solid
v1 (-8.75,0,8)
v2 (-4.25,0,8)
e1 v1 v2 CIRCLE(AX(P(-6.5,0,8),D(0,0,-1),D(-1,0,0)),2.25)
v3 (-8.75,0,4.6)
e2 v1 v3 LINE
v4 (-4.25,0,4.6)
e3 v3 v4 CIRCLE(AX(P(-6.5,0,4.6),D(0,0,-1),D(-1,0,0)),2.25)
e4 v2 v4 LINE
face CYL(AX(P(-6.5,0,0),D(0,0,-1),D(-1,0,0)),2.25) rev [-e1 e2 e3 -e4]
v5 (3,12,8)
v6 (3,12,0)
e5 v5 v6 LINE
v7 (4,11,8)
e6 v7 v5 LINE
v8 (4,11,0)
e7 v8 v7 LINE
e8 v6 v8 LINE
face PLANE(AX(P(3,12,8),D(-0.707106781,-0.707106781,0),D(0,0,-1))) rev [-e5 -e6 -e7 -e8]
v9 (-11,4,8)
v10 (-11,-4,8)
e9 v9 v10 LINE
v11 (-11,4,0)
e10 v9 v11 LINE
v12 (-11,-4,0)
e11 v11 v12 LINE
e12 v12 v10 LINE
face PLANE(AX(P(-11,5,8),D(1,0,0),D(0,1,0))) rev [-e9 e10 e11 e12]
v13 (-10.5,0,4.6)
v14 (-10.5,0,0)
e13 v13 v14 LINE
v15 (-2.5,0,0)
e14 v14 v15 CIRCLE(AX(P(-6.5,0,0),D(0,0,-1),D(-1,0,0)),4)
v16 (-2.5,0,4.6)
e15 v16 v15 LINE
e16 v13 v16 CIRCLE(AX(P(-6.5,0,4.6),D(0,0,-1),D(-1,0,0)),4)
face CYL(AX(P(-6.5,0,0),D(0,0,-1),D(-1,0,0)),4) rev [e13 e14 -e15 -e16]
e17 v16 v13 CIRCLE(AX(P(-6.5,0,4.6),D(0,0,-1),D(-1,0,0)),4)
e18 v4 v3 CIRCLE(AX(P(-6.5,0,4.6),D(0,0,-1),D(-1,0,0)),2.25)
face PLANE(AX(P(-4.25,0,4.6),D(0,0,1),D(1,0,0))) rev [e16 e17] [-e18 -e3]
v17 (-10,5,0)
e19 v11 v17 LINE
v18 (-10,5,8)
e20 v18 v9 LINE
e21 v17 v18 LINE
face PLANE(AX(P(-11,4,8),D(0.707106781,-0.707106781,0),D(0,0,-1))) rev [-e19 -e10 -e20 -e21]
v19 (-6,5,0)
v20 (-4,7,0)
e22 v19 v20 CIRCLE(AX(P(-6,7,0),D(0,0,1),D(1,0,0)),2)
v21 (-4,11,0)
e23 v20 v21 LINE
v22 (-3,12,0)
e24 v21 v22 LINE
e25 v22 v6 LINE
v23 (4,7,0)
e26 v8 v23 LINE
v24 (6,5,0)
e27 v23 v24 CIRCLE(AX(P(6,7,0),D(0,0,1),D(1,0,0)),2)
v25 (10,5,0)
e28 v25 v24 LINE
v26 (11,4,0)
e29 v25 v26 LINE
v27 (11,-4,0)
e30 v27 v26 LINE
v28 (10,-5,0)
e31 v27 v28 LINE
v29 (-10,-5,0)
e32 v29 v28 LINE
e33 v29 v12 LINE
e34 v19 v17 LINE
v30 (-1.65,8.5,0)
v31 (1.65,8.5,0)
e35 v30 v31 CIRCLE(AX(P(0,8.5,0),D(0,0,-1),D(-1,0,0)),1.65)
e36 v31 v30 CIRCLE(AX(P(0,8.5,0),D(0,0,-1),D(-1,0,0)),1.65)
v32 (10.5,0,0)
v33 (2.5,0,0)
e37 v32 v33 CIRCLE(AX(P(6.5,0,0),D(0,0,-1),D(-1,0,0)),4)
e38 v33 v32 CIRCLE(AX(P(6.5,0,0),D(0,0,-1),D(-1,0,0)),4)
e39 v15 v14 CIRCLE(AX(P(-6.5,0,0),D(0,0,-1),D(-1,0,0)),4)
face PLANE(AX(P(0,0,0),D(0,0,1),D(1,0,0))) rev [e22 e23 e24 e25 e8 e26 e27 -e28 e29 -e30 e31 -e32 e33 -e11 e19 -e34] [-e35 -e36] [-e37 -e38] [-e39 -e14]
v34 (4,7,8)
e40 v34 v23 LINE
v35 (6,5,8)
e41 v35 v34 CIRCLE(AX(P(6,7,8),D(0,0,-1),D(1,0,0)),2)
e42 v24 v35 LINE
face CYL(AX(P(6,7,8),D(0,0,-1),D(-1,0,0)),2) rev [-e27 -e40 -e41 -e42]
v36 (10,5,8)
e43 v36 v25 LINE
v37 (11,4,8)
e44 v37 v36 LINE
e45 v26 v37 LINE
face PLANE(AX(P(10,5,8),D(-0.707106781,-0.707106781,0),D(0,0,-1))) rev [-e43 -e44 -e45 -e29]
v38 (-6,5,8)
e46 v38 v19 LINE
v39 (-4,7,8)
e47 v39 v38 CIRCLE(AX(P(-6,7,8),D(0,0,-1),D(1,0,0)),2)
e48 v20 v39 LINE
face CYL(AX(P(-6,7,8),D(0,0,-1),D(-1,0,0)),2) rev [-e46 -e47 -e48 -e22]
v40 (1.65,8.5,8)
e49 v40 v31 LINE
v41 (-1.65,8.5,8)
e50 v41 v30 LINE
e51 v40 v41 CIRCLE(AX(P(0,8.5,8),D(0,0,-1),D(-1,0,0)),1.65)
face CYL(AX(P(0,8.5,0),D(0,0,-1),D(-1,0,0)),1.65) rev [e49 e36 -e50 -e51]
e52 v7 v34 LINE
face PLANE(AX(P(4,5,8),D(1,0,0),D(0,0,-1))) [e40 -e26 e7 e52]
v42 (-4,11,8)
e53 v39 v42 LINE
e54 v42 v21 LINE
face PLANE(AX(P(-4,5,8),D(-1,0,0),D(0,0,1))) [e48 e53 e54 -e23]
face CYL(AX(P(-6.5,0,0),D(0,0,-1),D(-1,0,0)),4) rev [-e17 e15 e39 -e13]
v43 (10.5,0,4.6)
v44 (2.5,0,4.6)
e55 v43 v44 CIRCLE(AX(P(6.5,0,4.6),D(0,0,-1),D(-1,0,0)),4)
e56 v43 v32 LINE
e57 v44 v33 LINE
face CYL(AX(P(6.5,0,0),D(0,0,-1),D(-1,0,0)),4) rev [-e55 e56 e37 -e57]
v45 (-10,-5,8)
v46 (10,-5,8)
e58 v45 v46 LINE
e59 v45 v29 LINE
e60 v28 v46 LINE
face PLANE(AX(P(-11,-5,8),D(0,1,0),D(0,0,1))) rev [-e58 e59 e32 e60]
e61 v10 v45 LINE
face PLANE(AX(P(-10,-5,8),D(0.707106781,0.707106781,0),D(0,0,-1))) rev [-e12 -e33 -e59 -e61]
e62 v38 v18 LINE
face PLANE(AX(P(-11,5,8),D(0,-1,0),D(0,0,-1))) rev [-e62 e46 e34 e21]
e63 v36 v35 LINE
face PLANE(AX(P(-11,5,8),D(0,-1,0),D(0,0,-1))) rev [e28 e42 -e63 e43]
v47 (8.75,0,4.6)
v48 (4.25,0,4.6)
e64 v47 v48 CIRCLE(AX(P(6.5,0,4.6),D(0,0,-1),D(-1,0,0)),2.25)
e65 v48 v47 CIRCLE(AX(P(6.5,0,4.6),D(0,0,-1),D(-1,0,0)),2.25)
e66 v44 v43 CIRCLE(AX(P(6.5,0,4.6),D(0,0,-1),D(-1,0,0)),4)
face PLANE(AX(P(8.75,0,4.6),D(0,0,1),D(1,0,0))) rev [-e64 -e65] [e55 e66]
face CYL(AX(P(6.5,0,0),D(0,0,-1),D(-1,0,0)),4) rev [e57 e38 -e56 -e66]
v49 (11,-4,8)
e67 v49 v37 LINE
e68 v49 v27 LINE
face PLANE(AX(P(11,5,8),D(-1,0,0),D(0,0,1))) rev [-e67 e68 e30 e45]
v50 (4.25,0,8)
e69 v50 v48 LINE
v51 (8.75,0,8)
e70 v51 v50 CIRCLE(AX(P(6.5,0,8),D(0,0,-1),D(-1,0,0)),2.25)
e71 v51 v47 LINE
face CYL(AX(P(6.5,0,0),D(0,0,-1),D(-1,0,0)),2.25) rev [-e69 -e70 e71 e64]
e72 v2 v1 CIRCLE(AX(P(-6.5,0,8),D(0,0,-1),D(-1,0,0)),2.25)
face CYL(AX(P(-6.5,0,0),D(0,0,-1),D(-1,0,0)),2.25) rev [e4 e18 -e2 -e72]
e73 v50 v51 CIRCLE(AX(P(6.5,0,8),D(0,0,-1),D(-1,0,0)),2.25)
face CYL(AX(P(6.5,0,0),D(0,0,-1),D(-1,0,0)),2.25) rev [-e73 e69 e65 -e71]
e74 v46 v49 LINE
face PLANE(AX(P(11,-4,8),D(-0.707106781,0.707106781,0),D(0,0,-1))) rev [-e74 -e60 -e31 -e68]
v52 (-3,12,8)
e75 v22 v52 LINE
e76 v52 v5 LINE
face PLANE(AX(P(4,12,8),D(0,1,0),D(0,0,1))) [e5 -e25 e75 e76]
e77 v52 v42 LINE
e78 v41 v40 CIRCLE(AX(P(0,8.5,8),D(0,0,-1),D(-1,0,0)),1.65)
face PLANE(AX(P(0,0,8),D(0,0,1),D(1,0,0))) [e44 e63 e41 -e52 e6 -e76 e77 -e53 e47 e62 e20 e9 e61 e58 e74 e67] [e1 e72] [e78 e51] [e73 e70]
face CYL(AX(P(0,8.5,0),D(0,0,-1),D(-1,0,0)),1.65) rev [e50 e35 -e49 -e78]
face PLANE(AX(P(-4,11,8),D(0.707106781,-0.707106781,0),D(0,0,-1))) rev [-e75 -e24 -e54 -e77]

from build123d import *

# Parameters (mm, degrees)
SKETCH1_W                                            = 22
SKETCH1_H                                            = 10
BOSS_EXTRUDE1_DEPTH                                  = 8
CBORE_FOR_M4_HEXAGON_SOCKET_HEAD_CAP_SCR_D           = 4.5
CBORE_FOR_M4_HEXAGON_SOCKET_HEAD_CAP_SCR_CBORE_D     = 8
CBORE_FOR_M4_HEXAGON_SOCKET_HEAD_CAP_SCR_CBORE_DEPTH = 4.6
SKETCH4_W                                            = 8
SKETCH4_H                                            = 7
BOSS_EXTRUDE2_DEPTH                                  = 8
M4_TAPPED_HOLE1_D                                    = 3.3
FILLET1_R                                            = 2
CHAMFER1_SIZE                                        = 1


with BuildPart() as part:
    # Sketch1 → Boss-Extrude1 (new body)
    with BuildSketch(Plane.XY):
        Rectangle(SKETCH1_W, SKETCH1_H)
    extrude(amount=BOSS_EXTRUDE1_DEPTH)

    # CBORE for M4 Hexagon socket head cap screws1 (through all)
    with Locations(Plane(origin=(0, 0, 0), x_dir=(-1, 0, 0), z_dir=(0, 0, -1))):
        with Locations((-6.5, 0), (6.5, 0)):
            CounterBoreHole(CBORE_FOR_M4_HEXAGON_SOCKET_HEAD_CAP_SCR_D / 2, CBORE_FOR_M4_HEXAGON_SOCKET_HEAD_CAP_SCR_CBORE_D / 2, CBORE_FOR_M4_HEXAGON_SOCKET_HEAD_CAP_SCR_CBORE_DEPTH)

    # Sketch4 → Boss-Extrude2 (add)
    with BuildSketch(Plane(origin=(0, 0, 0), x_dir=(-1, 0, 0), z_dir=(0, 0, -1))):
        with Locations((0, 8.5)):
            Rectangle(SKETCH4_W, SKETCH4_H)
    extrude(amount=-BOSS_EXTRUDE2_DEPTH)

    # M4 Tapped Hole1 (through all)
    with Locations(Plane(origin=(0, 0, 0), x_dir=(-1, 0, 0), z_dir=(0, 0, -1))):
        with Locations((0, 8.5)):
            Hole(M4_TAPPED_HOLE1_D / 2)

    # Fillet1
    fillet1_edges = [part.edges().sort_by_distance(p)[0] for p in [
        (4, 5, 4),
        (-4, 5, 4),
    ]]
    fillet(fillet1_edges, radius=FILLET1_R)

    # Chamfer1
    chamfer1_edges = [part.edges().sort_by_distance(p)[0] for p in [
        (4, 12, 4),
        (-4, 12, 4),
        (11, -5, 4),
        (-11, -5, 4),
        (-11, 5, 4),
        (11, 5, 4),
    ]]
    chamfer(chamfer1_edges, length=CHAMFER1_SIZE)


solid = part.part
